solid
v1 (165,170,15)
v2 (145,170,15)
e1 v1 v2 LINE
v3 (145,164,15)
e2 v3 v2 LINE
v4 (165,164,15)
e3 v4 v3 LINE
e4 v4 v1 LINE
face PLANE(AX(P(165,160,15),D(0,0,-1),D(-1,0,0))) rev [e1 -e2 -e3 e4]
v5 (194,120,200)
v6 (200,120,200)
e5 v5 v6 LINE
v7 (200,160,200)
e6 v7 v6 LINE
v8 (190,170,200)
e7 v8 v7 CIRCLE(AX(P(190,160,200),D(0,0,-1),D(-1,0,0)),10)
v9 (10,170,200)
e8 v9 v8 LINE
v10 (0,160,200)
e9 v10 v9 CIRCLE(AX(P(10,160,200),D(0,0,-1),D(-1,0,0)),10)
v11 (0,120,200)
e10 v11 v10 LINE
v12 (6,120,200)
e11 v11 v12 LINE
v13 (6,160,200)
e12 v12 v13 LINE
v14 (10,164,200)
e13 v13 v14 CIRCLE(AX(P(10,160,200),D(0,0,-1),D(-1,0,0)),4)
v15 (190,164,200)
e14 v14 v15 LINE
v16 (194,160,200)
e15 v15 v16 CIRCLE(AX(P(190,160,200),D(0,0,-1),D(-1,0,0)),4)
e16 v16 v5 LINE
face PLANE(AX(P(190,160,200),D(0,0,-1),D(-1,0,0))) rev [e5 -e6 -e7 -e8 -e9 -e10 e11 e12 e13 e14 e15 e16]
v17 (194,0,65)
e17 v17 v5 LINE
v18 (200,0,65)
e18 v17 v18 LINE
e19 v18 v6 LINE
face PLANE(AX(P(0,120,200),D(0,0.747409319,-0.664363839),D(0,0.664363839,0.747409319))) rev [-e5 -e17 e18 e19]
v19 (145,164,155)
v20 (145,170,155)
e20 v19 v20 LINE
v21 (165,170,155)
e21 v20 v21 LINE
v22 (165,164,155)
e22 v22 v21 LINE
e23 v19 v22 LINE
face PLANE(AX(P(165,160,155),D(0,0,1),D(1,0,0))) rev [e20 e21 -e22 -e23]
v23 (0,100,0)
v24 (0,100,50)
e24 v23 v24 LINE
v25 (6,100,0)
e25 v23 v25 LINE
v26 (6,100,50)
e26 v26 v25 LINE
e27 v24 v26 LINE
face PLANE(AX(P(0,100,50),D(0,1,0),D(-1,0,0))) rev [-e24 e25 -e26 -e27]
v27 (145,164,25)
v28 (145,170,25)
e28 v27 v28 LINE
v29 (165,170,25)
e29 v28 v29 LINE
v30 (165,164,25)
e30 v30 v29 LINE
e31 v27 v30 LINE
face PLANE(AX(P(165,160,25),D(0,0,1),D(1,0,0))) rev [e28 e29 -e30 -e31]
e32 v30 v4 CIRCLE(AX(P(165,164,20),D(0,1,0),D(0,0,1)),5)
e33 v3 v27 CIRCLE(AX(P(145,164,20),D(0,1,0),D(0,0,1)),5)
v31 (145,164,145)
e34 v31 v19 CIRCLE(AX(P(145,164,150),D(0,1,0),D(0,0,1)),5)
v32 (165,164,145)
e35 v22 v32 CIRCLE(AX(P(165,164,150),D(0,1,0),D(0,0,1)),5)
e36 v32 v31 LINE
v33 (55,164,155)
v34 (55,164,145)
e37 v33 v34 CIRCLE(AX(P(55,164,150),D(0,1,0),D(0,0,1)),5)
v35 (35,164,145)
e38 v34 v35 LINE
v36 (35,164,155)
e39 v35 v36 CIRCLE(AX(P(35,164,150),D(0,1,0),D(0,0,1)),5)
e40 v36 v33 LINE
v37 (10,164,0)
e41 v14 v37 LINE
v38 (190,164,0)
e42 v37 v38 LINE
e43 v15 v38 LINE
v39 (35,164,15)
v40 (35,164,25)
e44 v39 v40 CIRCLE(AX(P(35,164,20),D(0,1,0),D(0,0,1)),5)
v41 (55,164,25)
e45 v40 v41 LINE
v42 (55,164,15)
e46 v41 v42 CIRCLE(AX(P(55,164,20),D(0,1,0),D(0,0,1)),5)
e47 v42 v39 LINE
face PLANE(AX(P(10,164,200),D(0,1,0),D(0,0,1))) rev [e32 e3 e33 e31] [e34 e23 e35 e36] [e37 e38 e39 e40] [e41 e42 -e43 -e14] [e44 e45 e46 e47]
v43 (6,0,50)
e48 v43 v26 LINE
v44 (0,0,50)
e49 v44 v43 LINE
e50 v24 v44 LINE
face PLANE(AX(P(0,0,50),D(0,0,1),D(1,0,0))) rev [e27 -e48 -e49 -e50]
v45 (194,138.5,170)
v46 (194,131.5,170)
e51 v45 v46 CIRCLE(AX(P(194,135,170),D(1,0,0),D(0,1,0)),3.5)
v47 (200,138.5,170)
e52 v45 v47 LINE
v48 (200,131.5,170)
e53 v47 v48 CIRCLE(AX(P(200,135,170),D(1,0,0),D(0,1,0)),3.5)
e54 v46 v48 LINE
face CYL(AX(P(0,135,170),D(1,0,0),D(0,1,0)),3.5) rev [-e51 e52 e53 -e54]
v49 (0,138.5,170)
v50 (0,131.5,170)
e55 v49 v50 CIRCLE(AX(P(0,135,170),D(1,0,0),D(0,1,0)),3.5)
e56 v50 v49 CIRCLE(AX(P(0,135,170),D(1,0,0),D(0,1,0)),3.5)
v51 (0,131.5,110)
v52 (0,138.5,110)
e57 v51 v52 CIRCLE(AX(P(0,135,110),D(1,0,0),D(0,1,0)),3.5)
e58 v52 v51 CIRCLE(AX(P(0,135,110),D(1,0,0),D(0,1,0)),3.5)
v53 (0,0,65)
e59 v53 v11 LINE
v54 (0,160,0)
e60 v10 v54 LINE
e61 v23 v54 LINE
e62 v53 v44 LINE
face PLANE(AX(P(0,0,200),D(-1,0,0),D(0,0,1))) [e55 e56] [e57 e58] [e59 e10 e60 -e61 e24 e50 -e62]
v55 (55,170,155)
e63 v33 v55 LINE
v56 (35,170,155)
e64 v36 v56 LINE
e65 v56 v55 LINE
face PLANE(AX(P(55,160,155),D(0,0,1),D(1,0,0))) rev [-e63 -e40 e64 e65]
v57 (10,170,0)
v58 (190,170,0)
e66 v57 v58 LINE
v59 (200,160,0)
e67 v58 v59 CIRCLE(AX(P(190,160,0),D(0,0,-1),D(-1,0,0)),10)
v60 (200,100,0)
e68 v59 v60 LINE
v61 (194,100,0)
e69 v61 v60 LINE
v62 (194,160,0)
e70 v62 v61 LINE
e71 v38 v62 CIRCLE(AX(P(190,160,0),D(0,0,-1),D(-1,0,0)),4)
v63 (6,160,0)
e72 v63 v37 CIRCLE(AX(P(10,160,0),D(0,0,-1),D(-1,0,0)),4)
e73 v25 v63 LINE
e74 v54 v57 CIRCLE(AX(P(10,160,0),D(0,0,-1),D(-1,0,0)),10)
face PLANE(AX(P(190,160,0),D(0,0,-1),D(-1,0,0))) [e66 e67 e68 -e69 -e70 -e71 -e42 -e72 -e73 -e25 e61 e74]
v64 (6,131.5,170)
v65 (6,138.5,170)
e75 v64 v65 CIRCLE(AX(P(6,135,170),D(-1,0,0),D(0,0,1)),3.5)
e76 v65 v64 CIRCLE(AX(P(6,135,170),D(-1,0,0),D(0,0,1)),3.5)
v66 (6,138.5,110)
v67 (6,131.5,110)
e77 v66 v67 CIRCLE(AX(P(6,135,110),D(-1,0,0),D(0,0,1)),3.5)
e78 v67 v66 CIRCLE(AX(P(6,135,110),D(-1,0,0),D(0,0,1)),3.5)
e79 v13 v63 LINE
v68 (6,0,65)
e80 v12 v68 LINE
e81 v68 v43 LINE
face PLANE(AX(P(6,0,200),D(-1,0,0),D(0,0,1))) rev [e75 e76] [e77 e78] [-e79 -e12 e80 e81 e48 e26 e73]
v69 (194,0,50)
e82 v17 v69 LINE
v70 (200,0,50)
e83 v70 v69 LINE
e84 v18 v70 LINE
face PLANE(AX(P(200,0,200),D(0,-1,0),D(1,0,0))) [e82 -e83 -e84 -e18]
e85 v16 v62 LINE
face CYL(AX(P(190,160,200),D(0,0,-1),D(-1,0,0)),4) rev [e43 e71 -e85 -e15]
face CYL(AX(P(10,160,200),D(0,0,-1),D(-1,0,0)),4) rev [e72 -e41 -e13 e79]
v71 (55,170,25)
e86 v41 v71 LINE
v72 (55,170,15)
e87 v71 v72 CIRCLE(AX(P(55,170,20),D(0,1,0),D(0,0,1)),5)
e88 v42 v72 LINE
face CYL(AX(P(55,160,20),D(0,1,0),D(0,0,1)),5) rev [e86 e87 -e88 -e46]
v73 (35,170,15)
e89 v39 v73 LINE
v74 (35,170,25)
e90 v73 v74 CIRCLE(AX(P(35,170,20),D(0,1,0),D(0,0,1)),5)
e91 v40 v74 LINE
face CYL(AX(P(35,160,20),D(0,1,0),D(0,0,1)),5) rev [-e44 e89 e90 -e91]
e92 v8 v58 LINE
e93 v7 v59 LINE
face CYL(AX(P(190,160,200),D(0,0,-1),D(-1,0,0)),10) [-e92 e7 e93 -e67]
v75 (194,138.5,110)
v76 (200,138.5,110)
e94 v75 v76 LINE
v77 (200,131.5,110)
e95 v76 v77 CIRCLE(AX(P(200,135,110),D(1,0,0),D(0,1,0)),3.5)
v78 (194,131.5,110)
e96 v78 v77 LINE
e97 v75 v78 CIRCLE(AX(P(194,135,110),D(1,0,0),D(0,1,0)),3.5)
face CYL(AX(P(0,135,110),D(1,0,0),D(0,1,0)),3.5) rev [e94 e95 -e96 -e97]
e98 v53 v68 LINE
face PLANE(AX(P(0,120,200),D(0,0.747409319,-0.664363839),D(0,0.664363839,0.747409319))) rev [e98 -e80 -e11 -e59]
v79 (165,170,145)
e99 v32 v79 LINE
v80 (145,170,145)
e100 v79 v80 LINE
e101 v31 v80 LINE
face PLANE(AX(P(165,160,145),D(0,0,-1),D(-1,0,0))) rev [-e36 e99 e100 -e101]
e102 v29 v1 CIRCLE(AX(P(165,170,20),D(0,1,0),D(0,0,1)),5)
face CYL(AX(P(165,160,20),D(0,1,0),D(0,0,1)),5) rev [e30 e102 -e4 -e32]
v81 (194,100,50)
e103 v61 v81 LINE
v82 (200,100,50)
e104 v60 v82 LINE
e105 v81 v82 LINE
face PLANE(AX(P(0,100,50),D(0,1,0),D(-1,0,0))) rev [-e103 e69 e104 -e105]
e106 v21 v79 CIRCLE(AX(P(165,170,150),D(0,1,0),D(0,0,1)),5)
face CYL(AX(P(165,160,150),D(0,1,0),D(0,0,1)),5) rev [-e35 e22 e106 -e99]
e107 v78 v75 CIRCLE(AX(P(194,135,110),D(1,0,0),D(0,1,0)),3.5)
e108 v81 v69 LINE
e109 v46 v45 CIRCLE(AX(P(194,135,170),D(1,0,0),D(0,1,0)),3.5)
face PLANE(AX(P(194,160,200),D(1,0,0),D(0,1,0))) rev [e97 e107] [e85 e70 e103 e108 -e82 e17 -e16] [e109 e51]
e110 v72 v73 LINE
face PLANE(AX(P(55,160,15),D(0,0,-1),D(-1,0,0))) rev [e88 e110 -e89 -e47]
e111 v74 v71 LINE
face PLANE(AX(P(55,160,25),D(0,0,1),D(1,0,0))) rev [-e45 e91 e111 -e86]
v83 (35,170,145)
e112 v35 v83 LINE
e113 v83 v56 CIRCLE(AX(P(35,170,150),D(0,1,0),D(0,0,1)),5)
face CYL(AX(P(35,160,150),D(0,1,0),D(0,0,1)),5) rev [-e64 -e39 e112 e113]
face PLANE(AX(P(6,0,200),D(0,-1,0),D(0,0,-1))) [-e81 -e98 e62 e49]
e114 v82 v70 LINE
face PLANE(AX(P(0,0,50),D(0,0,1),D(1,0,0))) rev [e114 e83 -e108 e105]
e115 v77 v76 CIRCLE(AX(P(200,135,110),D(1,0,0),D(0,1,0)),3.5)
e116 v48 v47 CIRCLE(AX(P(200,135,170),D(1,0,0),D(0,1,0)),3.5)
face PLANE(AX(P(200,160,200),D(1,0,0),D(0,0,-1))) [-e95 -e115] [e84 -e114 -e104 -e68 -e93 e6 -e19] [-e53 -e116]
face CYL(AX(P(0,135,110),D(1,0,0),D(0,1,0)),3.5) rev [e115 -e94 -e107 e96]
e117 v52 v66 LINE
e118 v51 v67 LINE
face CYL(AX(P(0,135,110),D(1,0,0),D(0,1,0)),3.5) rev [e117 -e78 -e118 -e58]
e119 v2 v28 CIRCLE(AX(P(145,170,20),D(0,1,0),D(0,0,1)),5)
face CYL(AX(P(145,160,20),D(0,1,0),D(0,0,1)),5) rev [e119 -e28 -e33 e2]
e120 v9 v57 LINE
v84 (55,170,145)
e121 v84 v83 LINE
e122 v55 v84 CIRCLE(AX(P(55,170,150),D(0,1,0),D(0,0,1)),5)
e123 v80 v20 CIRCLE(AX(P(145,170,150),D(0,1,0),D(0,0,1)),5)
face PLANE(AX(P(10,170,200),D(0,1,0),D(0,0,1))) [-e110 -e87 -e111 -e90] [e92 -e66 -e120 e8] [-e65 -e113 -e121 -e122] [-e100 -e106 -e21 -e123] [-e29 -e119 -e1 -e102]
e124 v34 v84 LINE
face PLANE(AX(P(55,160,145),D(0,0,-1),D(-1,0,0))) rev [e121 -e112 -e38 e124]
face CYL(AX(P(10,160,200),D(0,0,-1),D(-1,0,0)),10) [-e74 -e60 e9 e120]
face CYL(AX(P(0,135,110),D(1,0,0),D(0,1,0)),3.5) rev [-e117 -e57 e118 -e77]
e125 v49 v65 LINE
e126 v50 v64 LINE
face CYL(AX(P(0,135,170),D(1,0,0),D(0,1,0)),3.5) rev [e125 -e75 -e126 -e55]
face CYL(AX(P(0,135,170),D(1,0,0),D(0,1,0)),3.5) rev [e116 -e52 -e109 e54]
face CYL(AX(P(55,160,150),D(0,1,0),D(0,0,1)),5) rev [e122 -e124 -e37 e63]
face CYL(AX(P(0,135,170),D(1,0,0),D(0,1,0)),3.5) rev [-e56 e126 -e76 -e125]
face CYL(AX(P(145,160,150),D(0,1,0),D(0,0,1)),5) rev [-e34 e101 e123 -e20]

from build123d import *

# Parameters (mm, degrees)
BOSS_EXTRUDE2_DEPTH = 200
CUT_EXTRUDE1_DEPTH  = 200
SKETCH3_R           = 3.5
CUT_EXTRUDE2_DEPTH  = 200
CUT_EXTRUDE3_DEPTH  = 10


with BuildPart() as part:
    # Sketch1 → Boss-Extrude2 (new body)
    with BuildSketch(Plane.XY):
        with BuildLine():
            Line((0, 0), (0, 160))
            ThreePointArc((0, 160), (2.928932188, 167.071067812), (10, 170))
            Line((10, 170), (190, 170))
            ThreePointArc((190, 170), (197.071067812, 167.071067812), (200, 160))
            Line((200, 160), (200, 0))
            Line((200, 0), (194, 0))
            Line((194, 0), (194, 160))
            ThreePointArc((194, 160), (192.828427125, 162.828427125), (190, 164))
            Line((190, 164), (10, 164))
            ThreePointArc((10, 164), (7.171572875, 162.828427125), (6, 160))
            Line((6, 160), (6, 0))
            Line((6, 0), (0, 0))
        make_face()
    extrude(amount=BOSS_EXTRUDE2_DEPTH)

    # Sketch2 → Cut-Extrude1 (cut)
    with BuildSketch(Plane(origin=(200, 0, 0), x_dir=(0, 0, -1), z_dir=(1, 0, 0))):
        Polygon((-200, 120), (-65, 0), (-50, 0), (-50, 100), (0, 100), (0, -9.162692683), (-225.149686355, -7.960981017), (-227.038090402, 77.768418596), align=None)
    extrude(amount=-CUT_EXTRUDE1_DEPTH, mode=Mode.SUBTRACT)

    # Sketch3 → Cut-Extrude2 (cut)
    with BuildSketch(Plane(origin=(200, 0, 0), x_dir=(0, 0, -1), z_dir=(1, 0, 0))):
        with Locations(Location((-170, 135, 0), (0, 0, 90))):
            Circle(SKETCH3_R)
        with Locations(Location((-110, 135, 0), (0, 0, 90))):
            Circle(SKETCH3_R)
    extrude(amount=-CUT_EXTRUDE2_DEPTH, mode=Mode.SUBTRACT)

    # Sketch4 → Cut-Extrude3 (cut)
    with BuildSketch(Plane(origin=(0, 170, 0), x_dir=(1, 0, 0), z_dir=(0, 1, 0))):
        with BuildLine():
            Line((165, -25), (145, -25))
            ThreePointArc((145, -25), (140, -20), (145, -15))
            Line((145, -15), (165, -15))
            ThreePointArc((165, -15), (170, -20), (165, -25))
        make_face()
        with BuildLine():
            Line((165, -155), (145, -155))
            ThreePointArc((145, -155), (140, -150), (145, -145))
            Line((145, -145), (165, -145))
            ThreePointArc((165, -145), (170, -150), (165, -155))
        make_face()
        with BuildLine():
            Line((55, -25), (35, -25))
            ThreePointArc((35, -25), (30, -20), (35, -15))
            Line((35, -15), (55, -15))
            ThreePointArc((55, -15), (60, -20), (55, -25))
        make_face()
        with BuildLine():
            Line((55, -155), (35, -155))
            ThreePointArc((35, -155), (30, -150), (35, -145))
            Line((35, -145), (55, -145))
            ThreePointArc((55, -145), (60, -150), (55, -155))
        make_face()
    extrude(amount=-CUT_EXTRUDE3_DEPTH, mode=Mode.SUBTRACT)


solid = part.part
